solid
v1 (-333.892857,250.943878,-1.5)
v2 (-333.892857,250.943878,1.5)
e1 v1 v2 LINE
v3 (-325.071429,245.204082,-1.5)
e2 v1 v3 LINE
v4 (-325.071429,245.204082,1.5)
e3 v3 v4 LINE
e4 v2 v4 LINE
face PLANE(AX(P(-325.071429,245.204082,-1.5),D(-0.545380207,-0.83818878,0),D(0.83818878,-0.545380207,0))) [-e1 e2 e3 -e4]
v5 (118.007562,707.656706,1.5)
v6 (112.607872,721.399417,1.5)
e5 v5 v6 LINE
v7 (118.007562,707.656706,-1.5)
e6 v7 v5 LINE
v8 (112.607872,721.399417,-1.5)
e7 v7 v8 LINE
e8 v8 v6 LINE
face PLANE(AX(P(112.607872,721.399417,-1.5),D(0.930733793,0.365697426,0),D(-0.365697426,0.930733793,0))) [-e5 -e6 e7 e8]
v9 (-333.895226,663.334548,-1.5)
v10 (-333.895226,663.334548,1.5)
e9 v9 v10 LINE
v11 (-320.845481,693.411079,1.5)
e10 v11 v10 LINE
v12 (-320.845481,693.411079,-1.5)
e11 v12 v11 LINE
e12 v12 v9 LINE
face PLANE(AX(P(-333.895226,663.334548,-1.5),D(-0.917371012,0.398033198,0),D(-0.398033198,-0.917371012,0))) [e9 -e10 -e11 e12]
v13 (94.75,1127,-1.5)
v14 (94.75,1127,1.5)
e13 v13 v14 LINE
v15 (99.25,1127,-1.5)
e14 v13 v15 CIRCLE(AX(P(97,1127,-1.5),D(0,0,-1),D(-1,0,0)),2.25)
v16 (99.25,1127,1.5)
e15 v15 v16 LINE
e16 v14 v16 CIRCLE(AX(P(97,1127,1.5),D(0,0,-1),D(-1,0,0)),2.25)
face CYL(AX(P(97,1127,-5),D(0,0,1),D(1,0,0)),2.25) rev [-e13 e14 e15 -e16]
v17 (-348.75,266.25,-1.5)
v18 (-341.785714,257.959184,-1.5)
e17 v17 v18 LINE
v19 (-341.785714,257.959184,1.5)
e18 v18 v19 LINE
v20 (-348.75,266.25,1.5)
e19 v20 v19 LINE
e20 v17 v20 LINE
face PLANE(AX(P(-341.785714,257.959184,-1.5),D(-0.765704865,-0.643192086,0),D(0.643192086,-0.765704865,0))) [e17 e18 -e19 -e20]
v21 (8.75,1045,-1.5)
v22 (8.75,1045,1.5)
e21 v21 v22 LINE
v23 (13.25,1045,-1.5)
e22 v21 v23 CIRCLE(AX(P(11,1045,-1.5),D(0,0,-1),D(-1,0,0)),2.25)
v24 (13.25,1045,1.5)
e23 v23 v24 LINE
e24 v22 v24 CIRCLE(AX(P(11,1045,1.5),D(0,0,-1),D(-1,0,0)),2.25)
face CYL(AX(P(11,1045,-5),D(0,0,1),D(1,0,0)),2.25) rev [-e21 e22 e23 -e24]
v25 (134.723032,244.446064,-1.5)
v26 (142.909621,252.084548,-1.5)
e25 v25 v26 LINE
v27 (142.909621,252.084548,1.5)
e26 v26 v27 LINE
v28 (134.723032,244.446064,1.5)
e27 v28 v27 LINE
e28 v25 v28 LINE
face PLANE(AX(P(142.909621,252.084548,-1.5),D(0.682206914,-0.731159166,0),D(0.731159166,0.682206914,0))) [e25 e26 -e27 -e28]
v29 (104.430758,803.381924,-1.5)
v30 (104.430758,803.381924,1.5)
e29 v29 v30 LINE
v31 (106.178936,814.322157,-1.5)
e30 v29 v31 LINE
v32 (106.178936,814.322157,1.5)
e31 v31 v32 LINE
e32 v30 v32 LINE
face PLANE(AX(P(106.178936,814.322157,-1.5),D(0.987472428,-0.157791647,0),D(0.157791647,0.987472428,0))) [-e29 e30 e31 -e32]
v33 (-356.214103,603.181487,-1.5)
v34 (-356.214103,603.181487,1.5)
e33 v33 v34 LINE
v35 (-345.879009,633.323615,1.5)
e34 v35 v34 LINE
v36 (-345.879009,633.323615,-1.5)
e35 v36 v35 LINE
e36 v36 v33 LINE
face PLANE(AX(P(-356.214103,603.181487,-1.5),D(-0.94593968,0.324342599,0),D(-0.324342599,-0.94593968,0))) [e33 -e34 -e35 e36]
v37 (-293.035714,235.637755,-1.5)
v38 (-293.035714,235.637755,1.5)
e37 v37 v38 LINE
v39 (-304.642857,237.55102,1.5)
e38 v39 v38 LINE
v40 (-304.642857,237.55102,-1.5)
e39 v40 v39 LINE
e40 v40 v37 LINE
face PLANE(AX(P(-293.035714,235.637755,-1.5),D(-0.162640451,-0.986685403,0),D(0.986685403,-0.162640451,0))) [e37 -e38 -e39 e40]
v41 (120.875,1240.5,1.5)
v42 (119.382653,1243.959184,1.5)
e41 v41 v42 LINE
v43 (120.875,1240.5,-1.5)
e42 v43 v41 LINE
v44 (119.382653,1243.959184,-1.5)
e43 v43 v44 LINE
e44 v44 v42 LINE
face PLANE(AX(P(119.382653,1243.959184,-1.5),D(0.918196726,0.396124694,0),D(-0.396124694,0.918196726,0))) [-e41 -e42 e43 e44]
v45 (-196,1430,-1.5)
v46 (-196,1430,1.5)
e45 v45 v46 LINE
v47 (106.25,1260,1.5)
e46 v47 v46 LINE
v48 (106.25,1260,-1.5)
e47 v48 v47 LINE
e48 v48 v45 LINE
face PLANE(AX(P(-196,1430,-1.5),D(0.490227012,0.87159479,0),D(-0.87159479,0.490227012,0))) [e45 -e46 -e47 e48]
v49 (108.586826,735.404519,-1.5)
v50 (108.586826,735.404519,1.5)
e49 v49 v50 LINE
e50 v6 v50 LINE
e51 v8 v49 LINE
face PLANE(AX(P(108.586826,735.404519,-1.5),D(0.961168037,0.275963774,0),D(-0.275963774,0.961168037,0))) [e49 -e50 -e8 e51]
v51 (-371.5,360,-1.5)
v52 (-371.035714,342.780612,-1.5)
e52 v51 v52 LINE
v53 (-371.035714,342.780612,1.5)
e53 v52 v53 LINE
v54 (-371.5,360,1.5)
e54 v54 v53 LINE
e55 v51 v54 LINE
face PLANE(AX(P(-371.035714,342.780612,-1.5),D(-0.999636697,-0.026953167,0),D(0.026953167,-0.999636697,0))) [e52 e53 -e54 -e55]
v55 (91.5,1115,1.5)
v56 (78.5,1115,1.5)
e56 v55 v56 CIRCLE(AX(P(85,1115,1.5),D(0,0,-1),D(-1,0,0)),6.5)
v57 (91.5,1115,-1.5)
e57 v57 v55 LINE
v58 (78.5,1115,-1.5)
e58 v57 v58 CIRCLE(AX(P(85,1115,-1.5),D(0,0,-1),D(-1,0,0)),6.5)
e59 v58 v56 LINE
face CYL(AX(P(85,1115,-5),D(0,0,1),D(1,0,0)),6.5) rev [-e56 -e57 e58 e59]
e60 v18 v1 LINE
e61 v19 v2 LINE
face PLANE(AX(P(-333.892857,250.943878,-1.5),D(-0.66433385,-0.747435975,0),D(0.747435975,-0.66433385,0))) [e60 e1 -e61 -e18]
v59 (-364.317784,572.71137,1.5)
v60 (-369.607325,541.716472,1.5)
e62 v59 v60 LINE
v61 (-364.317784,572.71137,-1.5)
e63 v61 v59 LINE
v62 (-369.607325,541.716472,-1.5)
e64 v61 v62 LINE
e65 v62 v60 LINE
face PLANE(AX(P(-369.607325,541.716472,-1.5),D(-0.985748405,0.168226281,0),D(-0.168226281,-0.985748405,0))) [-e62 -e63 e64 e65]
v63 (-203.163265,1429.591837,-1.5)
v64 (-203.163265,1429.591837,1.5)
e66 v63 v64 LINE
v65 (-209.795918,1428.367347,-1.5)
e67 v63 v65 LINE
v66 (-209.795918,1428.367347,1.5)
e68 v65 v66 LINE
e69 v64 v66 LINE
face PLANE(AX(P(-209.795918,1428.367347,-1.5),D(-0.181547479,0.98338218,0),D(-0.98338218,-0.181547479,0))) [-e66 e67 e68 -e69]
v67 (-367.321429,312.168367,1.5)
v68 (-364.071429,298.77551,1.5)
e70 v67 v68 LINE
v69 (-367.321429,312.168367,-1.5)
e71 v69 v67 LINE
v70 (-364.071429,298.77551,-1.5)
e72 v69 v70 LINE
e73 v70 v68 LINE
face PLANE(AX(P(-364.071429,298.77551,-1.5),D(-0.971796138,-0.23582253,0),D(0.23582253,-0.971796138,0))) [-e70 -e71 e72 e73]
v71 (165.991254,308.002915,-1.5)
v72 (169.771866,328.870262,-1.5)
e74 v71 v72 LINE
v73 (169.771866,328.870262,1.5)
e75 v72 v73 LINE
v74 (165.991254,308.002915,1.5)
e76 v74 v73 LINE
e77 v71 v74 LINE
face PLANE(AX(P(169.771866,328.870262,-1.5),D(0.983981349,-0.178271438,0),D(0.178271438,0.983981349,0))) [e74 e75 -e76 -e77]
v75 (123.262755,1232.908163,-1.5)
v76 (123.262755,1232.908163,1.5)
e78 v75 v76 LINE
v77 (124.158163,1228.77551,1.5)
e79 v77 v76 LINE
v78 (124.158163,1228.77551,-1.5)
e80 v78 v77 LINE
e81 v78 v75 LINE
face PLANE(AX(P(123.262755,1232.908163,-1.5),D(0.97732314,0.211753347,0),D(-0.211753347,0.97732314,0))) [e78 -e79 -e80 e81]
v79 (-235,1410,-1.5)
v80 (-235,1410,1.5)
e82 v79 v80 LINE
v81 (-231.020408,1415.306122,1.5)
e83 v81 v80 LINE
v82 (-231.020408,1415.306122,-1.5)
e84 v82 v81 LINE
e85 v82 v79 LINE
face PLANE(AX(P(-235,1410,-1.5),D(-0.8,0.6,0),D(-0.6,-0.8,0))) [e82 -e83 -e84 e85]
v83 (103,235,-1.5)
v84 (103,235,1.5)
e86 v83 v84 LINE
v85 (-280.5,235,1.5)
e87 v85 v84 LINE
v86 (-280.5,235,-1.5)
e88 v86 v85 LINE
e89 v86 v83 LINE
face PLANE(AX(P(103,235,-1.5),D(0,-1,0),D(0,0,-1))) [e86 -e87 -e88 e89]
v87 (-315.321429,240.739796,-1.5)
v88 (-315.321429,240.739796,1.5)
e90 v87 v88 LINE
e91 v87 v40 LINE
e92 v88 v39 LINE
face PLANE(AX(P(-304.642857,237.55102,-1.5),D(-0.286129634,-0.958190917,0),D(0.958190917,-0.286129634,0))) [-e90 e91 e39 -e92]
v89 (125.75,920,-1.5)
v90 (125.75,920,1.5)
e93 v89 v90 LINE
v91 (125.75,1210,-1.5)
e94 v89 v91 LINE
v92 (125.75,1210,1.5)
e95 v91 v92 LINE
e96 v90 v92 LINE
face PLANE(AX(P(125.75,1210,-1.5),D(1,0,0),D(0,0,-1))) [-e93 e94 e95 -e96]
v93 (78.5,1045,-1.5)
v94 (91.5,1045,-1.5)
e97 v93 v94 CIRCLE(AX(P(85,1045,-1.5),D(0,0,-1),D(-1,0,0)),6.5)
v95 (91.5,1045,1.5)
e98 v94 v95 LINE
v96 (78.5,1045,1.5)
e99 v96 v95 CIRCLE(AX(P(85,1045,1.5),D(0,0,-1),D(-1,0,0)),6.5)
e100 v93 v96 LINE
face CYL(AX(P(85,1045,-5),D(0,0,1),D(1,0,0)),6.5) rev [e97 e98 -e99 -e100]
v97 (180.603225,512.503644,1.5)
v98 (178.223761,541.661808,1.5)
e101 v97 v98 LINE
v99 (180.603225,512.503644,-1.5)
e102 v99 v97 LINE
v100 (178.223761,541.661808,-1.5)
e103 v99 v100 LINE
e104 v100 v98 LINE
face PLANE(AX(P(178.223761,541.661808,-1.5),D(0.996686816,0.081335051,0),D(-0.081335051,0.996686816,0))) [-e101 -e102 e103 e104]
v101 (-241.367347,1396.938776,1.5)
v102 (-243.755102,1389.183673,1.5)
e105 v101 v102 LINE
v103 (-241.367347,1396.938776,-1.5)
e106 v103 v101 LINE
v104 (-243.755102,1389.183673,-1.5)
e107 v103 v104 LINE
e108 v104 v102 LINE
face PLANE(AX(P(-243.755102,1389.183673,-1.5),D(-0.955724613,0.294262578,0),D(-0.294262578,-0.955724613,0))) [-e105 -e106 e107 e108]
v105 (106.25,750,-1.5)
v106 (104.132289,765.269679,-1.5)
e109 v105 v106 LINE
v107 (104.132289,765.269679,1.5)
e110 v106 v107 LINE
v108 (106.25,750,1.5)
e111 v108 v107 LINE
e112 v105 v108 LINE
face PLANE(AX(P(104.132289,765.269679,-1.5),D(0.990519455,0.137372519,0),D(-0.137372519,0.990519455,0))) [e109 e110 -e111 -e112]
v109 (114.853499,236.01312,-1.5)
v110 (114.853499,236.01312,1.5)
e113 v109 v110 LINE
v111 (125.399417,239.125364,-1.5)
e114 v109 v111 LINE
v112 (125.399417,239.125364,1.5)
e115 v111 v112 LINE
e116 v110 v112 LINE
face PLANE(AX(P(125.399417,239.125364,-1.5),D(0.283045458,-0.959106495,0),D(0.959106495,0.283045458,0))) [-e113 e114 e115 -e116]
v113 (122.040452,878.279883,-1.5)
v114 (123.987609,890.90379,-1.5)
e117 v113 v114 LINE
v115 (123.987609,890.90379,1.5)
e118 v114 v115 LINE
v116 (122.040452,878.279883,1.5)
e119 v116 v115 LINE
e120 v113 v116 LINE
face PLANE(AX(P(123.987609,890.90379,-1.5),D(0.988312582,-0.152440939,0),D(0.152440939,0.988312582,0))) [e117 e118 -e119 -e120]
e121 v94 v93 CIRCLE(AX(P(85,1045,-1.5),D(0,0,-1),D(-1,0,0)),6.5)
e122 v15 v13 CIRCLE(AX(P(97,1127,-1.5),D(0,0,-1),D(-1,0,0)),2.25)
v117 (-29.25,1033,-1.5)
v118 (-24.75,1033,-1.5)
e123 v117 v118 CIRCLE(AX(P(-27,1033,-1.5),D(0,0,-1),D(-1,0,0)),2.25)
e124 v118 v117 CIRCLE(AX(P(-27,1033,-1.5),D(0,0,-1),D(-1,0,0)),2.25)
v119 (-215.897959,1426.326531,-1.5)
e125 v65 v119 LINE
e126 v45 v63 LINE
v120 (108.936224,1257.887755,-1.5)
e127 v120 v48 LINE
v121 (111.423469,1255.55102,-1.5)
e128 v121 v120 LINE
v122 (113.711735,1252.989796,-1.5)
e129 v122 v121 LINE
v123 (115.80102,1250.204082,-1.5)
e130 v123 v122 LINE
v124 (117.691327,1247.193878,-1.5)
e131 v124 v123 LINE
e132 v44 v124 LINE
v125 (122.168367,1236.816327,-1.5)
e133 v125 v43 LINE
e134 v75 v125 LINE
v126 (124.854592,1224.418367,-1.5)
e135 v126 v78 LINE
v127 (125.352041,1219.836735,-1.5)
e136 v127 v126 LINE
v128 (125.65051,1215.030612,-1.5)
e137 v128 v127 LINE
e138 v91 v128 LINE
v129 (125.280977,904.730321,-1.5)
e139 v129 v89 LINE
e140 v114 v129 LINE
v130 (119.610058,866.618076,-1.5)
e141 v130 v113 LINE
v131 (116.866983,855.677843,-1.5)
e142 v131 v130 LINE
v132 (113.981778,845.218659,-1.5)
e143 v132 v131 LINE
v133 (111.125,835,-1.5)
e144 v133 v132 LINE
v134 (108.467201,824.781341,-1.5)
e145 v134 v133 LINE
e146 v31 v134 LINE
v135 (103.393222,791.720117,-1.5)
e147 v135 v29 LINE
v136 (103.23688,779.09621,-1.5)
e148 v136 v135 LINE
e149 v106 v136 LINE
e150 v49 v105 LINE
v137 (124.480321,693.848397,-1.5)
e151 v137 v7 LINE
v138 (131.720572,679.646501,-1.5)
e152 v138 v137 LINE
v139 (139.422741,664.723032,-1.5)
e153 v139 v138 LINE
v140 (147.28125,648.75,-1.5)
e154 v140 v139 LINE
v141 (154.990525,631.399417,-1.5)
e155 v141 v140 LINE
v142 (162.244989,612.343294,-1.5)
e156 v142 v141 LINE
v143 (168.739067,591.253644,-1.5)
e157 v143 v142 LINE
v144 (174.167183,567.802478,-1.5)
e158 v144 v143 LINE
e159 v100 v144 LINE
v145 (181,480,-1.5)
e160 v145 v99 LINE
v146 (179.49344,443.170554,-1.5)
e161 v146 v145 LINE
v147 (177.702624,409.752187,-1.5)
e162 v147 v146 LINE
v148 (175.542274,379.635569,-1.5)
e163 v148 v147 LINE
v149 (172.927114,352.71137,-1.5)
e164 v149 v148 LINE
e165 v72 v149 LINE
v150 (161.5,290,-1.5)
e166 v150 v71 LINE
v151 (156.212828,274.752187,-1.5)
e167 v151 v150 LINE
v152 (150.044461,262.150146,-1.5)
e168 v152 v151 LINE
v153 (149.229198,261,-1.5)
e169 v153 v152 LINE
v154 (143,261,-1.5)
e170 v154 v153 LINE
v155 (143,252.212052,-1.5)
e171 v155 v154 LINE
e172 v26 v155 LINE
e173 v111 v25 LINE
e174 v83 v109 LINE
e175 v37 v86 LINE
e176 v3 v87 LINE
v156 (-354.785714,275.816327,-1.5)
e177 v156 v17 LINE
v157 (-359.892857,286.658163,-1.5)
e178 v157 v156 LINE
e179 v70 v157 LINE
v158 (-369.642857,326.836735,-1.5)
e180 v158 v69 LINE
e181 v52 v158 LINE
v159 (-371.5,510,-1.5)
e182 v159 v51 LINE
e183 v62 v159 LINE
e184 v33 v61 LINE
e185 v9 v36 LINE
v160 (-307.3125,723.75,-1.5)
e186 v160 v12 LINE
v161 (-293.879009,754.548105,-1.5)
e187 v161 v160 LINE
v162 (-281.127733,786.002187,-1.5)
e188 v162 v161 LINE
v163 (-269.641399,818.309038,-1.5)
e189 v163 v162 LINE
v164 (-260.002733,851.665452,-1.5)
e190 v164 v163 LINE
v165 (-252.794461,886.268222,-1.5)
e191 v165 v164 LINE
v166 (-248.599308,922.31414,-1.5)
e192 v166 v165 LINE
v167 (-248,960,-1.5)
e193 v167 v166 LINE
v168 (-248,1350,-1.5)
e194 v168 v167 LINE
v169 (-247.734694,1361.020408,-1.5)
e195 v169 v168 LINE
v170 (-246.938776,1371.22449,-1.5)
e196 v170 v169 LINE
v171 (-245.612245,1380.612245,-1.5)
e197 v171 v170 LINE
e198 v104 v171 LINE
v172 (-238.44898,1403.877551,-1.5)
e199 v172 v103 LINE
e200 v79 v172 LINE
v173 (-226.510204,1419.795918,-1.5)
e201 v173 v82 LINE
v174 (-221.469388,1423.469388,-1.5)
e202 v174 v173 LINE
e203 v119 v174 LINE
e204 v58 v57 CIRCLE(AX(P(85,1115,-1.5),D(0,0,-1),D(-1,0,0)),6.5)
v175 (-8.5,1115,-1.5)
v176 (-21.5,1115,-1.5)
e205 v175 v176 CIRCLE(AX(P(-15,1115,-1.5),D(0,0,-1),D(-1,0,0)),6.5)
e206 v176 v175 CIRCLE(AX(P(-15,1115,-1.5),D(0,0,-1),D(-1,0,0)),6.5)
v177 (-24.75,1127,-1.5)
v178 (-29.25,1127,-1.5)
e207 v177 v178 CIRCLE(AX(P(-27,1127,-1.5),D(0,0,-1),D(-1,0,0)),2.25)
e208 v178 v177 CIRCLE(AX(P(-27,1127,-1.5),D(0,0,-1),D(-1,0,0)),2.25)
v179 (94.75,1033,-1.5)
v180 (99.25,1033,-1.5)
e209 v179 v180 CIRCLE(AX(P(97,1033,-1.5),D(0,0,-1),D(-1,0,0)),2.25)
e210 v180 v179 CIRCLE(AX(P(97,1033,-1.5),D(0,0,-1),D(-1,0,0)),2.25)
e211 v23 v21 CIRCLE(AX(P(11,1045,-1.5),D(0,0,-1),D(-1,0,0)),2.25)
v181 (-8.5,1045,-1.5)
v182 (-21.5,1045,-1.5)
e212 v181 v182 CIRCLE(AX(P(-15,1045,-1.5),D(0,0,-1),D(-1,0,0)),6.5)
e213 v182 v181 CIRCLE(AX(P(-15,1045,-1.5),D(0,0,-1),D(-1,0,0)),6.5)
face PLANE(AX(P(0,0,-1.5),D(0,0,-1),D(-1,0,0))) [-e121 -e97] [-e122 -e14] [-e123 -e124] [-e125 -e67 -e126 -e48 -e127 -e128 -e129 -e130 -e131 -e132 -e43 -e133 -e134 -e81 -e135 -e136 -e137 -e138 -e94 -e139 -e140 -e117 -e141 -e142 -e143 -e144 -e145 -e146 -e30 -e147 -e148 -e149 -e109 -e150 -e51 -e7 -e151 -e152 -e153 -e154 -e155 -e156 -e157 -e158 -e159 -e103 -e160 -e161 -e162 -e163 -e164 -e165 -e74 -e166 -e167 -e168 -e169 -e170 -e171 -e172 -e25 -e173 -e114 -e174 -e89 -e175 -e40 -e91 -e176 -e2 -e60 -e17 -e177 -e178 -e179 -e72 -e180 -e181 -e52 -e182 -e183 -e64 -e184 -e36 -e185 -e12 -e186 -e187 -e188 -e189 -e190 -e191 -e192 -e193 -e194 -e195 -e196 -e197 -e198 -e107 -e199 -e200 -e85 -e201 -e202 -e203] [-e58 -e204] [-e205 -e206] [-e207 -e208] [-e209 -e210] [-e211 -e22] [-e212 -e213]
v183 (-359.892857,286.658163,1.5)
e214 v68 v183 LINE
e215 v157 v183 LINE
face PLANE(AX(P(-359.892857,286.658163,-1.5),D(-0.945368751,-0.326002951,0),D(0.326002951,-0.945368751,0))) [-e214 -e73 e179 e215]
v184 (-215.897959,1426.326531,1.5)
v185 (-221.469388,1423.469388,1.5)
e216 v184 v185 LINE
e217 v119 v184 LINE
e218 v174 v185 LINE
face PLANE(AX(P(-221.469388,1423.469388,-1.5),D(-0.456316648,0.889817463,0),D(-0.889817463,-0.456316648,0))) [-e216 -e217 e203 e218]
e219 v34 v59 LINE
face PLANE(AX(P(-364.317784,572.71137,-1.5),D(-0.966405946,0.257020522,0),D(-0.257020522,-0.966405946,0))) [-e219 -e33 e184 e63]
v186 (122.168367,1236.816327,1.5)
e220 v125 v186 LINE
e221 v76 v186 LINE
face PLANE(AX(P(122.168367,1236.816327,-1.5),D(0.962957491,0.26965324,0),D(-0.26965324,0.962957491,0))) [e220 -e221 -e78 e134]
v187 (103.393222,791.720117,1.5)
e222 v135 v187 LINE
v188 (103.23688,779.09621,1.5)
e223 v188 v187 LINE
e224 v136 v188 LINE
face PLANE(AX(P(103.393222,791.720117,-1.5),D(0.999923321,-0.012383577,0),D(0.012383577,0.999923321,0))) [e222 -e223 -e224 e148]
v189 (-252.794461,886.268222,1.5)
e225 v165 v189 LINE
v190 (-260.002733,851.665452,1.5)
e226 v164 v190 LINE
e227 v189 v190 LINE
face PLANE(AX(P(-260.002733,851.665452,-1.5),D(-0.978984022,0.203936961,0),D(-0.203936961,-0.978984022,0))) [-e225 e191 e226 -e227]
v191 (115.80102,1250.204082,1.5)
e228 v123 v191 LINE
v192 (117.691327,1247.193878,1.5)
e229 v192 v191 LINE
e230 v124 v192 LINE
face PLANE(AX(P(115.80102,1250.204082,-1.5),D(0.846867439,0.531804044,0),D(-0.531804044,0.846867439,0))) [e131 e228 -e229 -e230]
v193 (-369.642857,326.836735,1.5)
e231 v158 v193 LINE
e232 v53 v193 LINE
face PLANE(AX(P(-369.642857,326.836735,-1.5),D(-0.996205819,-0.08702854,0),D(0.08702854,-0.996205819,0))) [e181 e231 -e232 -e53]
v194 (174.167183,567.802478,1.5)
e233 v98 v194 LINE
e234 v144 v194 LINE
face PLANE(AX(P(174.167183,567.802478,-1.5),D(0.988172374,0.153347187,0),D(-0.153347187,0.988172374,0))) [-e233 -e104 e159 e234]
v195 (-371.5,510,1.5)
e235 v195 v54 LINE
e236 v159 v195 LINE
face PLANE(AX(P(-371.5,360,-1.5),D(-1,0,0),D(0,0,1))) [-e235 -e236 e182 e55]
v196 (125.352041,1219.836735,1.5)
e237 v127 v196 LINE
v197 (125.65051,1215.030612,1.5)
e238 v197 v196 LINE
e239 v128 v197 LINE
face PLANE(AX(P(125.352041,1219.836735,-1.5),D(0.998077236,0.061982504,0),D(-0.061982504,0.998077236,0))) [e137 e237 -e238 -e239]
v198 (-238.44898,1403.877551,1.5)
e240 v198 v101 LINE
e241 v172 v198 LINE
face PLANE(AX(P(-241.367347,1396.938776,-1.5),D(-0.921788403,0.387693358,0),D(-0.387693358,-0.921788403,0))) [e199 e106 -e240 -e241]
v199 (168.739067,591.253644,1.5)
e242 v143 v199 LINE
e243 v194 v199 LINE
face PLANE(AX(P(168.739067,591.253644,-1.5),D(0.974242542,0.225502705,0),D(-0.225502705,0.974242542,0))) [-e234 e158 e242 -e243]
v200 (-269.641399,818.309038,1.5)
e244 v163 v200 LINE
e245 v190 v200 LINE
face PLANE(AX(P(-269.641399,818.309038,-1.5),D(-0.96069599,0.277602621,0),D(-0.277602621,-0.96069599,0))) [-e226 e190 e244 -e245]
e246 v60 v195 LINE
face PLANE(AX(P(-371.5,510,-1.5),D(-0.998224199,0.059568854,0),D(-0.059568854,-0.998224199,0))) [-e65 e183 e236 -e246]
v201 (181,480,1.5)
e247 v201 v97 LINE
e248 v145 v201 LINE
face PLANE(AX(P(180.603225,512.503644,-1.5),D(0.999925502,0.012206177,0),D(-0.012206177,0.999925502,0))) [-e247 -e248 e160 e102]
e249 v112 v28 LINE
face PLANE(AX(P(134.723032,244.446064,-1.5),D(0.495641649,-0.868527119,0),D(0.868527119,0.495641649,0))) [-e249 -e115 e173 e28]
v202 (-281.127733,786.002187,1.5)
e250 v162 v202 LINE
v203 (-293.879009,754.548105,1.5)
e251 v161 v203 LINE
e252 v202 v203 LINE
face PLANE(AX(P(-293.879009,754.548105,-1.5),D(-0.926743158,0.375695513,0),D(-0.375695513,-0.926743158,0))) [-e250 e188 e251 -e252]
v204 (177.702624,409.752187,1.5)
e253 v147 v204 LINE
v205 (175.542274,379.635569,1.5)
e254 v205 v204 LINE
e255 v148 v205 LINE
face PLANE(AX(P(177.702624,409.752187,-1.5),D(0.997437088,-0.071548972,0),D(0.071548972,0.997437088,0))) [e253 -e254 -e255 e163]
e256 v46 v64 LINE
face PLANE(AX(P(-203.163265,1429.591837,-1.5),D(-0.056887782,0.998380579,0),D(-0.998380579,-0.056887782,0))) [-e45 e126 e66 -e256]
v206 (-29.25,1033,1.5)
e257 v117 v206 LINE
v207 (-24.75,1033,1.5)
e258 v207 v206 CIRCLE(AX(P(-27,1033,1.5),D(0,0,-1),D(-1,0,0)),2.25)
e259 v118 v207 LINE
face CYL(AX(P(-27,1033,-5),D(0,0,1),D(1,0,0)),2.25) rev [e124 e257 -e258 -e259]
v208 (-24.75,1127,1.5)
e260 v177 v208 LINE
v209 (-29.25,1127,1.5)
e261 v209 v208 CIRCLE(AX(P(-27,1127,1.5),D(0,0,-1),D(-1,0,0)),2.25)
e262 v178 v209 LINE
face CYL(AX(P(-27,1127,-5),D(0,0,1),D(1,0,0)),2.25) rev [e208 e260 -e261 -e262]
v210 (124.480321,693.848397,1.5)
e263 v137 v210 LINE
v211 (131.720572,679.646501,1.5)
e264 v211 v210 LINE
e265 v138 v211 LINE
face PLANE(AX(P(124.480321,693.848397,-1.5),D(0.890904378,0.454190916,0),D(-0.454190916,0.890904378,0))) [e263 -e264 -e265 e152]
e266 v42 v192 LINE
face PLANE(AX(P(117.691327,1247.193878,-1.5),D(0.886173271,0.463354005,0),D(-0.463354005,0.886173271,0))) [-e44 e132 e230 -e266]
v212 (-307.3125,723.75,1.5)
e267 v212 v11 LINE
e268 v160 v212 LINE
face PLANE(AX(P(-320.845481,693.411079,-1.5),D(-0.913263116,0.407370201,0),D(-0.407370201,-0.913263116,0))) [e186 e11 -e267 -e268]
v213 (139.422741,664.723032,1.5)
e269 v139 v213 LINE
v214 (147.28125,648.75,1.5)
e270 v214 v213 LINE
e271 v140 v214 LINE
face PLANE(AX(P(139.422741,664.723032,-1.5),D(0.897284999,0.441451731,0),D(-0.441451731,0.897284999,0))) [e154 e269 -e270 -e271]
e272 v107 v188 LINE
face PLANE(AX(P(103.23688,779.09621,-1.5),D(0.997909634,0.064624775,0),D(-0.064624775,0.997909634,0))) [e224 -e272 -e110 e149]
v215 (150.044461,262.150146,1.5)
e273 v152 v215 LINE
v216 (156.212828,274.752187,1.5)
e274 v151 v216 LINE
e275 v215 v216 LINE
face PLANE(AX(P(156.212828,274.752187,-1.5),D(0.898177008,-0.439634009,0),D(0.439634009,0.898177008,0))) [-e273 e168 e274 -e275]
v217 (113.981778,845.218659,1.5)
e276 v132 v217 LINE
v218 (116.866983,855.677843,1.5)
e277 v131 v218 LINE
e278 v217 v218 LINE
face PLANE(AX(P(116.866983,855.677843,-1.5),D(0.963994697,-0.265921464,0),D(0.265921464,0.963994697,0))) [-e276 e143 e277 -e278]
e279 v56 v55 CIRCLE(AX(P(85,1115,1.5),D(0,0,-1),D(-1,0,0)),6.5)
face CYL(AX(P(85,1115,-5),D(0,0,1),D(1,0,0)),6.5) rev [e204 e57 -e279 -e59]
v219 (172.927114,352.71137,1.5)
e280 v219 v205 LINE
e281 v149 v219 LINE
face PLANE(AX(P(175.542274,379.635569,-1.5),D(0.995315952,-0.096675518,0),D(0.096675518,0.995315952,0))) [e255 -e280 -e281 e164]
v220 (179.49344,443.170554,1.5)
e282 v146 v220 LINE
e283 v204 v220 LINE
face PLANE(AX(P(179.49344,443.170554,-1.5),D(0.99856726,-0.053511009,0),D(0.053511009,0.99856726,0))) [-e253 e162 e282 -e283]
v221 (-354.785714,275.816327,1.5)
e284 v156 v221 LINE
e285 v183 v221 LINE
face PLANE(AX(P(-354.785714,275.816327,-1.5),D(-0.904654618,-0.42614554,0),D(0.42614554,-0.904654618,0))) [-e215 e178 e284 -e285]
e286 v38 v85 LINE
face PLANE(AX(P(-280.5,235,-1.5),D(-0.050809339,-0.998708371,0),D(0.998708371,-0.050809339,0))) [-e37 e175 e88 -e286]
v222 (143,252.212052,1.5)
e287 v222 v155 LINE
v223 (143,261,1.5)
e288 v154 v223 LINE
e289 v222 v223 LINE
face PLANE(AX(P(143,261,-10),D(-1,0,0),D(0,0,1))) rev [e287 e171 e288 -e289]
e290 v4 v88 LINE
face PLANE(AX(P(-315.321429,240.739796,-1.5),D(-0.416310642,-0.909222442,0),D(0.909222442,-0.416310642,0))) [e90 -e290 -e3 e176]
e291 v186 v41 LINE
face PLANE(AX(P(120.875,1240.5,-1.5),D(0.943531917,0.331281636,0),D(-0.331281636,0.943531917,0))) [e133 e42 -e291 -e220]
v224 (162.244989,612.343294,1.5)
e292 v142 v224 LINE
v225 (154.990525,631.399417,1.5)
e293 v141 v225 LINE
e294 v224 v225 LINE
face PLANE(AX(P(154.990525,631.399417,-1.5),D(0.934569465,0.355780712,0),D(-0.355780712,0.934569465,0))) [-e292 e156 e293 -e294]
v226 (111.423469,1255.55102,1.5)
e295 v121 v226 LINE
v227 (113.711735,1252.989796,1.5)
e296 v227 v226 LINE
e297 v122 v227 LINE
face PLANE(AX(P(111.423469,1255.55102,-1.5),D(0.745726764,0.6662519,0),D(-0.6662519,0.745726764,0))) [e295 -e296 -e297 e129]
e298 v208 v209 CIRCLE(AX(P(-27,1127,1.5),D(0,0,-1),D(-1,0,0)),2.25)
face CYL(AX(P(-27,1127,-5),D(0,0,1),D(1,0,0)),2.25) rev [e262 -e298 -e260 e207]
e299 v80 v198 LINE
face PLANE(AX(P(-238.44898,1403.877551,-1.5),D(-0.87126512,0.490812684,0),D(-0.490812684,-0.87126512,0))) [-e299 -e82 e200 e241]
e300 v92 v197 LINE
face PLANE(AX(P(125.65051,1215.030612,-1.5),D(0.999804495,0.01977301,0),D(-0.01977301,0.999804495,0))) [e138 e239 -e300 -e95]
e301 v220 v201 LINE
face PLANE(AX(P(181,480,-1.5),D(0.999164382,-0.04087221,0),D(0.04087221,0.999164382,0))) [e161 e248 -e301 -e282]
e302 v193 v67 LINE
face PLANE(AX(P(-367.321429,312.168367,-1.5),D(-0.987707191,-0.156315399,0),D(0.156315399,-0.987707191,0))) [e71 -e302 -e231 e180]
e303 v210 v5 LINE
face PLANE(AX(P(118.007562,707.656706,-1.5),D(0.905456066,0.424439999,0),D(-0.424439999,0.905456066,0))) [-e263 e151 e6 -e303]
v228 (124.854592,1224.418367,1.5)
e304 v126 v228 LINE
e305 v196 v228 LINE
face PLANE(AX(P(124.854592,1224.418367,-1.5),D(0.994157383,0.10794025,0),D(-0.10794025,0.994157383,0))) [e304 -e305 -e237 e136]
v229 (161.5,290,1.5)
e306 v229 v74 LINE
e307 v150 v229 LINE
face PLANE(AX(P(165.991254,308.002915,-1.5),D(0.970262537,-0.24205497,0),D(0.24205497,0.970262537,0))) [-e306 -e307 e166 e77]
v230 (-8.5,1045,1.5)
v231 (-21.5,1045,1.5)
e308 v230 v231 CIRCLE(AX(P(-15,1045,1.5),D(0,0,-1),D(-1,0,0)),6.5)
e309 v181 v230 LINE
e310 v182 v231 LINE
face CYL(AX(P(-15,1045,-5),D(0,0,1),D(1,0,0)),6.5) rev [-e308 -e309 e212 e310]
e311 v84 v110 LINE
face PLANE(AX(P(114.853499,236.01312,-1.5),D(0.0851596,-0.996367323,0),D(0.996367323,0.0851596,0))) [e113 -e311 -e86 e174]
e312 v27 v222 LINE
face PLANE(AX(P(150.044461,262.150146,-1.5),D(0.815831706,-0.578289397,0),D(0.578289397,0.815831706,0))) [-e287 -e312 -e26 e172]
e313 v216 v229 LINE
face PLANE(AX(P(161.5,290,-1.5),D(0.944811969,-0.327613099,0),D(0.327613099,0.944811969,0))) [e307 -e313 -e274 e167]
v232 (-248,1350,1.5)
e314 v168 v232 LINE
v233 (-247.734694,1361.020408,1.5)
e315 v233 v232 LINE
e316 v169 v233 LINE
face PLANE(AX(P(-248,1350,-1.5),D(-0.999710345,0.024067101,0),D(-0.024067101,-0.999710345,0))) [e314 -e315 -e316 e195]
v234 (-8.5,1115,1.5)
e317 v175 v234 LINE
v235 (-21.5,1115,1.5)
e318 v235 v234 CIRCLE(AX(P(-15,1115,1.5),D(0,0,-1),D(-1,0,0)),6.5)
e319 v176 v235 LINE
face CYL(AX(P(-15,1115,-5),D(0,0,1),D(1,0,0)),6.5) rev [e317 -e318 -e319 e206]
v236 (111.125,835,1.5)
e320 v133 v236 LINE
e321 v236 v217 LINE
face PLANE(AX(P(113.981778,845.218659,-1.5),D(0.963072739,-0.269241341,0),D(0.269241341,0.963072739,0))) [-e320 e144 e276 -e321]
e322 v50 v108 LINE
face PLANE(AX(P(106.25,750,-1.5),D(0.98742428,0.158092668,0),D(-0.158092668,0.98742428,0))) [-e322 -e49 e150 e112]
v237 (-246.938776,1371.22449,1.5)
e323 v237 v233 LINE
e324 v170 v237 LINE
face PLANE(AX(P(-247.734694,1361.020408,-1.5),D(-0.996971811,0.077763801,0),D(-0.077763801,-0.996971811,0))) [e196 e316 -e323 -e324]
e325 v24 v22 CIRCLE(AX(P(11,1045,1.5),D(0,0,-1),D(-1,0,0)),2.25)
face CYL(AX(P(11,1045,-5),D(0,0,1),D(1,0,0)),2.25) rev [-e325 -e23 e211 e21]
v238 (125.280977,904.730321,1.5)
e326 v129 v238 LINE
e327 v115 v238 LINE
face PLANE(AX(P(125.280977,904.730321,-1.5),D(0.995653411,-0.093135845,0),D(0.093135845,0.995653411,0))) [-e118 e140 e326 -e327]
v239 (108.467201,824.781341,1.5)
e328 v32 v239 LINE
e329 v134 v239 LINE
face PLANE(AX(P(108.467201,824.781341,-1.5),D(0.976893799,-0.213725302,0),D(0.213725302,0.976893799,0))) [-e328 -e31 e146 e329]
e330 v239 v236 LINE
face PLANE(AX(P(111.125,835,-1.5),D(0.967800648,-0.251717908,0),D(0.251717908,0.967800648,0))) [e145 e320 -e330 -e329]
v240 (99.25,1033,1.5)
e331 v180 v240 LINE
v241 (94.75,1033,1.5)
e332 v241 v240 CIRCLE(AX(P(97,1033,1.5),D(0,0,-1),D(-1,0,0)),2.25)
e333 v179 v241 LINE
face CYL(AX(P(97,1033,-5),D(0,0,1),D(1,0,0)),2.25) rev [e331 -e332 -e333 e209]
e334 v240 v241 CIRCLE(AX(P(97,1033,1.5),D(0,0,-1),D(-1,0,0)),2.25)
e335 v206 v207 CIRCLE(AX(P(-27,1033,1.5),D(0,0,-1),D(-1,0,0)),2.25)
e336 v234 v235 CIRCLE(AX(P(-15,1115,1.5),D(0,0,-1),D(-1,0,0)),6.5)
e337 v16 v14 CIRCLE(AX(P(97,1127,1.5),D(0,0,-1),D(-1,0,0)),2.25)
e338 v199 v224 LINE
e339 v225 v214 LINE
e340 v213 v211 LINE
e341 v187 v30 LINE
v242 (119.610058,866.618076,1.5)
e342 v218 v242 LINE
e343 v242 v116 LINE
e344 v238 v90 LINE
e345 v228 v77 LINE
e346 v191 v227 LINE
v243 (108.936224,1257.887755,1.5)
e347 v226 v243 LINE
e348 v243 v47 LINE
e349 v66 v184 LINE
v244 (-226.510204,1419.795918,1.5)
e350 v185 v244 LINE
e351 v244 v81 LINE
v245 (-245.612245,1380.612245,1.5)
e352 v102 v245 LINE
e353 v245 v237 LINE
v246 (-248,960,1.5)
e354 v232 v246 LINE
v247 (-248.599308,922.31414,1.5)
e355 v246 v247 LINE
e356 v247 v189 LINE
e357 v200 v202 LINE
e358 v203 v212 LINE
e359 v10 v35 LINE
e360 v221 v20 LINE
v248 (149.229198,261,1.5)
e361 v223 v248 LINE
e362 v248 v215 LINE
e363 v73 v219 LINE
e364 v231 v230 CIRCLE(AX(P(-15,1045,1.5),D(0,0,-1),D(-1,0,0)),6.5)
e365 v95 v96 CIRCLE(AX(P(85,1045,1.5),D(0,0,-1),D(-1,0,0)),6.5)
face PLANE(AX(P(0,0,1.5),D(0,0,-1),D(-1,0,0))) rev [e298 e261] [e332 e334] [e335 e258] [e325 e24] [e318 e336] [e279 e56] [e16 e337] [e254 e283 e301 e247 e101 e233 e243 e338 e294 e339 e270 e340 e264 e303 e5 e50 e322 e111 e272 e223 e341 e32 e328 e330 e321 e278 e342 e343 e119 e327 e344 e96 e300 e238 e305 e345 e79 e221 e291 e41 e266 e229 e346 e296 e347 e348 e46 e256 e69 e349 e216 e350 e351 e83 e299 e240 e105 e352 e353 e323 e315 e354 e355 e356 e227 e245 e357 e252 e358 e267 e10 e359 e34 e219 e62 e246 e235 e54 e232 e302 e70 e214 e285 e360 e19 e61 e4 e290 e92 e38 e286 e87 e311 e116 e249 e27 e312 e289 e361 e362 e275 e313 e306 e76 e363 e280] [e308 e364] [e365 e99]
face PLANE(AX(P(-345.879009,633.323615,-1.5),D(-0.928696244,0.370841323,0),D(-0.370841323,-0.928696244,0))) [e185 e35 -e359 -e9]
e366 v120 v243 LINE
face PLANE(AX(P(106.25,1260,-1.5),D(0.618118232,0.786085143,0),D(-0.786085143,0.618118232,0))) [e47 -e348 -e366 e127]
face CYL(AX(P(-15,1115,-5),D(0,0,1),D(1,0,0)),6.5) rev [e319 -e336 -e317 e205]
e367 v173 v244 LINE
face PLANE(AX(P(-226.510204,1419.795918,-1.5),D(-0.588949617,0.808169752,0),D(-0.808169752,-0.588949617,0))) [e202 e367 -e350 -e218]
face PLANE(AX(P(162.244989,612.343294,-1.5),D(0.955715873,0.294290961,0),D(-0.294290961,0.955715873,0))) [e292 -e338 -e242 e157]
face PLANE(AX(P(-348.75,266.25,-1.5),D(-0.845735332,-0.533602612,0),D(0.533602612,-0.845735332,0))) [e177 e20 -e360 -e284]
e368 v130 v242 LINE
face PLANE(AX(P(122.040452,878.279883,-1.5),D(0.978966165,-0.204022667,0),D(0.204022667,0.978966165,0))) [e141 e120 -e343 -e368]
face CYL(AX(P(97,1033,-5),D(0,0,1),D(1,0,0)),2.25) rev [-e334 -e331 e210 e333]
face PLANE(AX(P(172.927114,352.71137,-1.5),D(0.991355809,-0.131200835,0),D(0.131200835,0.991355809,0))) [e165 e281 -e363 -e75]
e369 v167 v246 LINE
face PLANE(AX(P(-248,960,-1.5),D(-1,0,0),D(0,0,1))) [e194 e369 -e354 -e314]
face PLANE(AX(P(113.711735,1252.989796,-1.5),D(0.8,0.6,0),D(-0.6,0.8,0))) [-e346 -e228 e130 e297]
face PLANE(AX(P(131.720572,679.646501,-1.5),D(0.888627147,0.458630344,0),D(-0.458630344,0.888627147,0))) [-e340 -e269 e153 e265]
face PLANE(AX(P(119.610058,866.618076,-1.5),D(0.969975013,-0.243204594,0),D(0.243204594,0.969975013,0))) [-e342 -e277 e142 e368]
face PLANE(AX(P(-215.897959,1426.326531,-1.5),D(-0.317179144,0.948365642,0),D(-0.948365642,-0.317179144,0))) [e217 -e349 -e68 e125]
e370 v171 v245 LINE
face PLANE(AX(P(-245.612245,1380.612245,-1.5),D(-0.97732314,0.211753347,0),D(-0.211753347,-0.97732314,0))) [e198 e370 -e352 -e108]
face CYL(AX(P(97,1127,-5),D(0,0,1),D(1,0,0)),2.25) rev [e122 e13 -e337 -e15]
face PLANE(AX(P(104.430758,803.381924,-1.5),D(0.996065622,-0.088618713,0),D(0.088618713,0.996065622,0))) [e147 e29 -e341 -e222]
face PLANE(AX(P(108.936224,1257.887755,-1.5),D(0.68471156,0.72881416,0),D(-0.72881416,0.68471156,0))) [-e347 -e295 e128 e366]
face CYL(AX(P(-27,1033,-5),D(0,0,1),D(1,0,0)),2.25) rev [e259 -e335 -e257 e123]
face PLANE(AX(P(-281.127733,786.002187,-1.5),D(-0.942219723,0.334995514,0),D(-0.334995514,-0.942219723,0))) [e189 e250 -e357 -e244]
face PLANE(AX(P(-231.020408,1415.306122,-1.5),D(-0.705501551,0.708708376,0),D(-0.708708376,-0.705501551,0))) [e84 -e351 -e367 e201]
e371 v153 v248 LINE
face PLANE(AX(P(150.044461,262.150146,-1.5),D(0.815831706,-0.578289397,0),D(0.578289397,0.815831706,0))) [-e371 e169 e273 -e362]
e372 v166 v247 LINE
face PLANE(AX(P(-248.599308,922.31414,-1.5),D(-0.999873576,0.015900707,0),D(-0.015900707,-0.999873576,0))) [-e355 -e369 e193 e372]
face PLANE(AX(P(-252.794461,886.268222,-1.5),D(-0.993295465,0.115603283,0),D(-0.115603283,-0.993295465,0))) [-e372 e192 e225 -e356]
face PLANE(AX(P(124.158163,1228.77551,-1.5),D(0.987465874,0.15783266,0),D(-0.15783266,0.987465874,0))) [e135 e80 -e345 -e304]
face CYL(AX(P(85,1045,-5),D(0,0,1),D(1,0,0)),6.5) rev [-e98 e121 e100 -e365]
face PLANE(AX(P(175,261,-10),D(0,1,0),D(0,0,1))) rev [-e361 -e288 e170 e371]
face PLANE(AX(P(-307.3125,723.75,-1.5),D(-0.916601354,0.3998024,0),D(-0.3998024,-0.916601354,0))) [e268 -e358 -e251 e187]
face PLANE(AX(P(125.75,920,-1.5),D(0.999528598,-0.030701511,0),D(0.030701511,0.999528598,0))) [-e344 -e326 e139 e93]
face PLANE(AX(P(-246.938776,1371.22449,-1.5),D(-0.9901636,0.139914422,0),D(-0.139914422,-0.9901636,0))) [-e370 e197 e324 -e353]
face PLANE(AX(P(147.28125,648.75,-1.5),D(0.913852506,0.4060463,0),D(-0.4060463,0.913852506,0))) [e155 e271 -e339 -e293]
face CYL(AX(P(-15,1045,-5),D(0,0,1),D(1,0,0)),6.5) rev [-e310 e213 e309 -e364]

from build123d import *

# Parameters (mm, degrees)
EXTRUDE_1_DEPTH     = 1.5
SKETCH_2_W          = 32
SKETCH_2_H          = 22
CUT_EXTRUDE_1_DEPTH = 10
SKETCH_3_R          = 2.25
SKETCH_3_R_2        = 6.5
CUT_EXTRUDE_2_DEPTH = 5


with BuildPart() as part:
    # 草图1 → 凸台-拉伸1 (new, symmetric)
    with BuildSketch(Plane.XY):
        Polygon((103, 235), (-24.833333333, 235), (-152.666666667, 235), (-280.5, 235), (-293.035714286, 235.637755102), (-304.642857143, 237.551020408), (-315.321428571, 240.739795918), (-325.071428571, 245.204081633), (-333.892857143, 250.943877551), (-341.785714286, 257.959183673), (-348.75, 266.25), (-354.785714286, 275.816326531), (-359.892857143, 286.658163265), (-364.071428571, 298.775510204), (-367.321428571, 312.168367347), (-369.642857143, 326.836734694), (-371.035714286, 342.780612245), (-371.5, 360), (-371.5, 410), (-371.5, 460), (-371.5, 510), (-369.607325073, 541.716472303), (-364.317784257, 572.711370262), (-356.214103499, 603.18148688), (-345.879008746, 633.32361516), (-333.895225948, 663.334548105), (-320.84548105, 693.411078717), (-307.3125, 723.75), (-293.879008746, 754.548104956), (-281.127733236, 786.002186589), (-269.641399417, 818.309037901), (-260.002733236, 851.665451895), (-252.794460641, 886.268221574), (-248.59930758, 922.314139942), (-248, 960), (-248, 1090), (-248, 1220), (-248, 1350), (-247.734693878, 1361.020408163), (-246.93877551, 1371.224489796), (-245.612244898, 1380.612244898), (-243.755102041, 1389.183673469), (-241.367346939, 1396.93877551), (-238.448979592, 1403.87755102), (-235, 1410), (-231.020408163, 1415.306122449), (-226.510204082, 1419.795918367), (-221.469387755, 1423.469387755), (-215.897959184, 1426.326530612), (-209.795918367, 1428.367346939), (-203.163265306, 1429.591836735), (-196, 1430), (-95.25, 1373.333333333), (5.5, 1316.666666667), (106.25, 1260), (108.93622449, 1257.887755102), (111.423469388, 1255.551020408), (113.711734694, 1252.989795918), (115.801020408, 1250.204081633), (117.691326531, 1247.193877551), (119.382653061, 1243.959183673), (120.875, 1240.5), (122.168367347, 1236.816326531), (123.262755102, 1232.908163265), (124.158163265, 1228.775510204), (124.854591837, 1224.418367347), (125.352040816, 1219.836734694), (125.650510204, 1215.030612245), (125.75, 1210), (125.75, 1113.333333333), (125.75, 1016.666666667), (125.75, 920), (125.280976676, 904.7303207), (123.987609329, 890.903790087), (122.040451895, 878.279883382), (119.610058309, 866.618075802), (116.866982507, 855.677842566), (113.981778426, 845.218658892), (111.125, 835), (108.467201166, 824.781341108), (106.17893586, 814.322157434), (104.430758017, 803.381924198), (103.393221574, 791.720116618), (103.236880466, 779.096209913), (104.13228863, 765.2696793), (106.25, 750), (108.586825802, 735.40451895), (112.60787172, 721.39941691), (118.007561953, 707.656705539), (124.4803207, 693.848396501), (131.720572157, 679.646501458), (139.422740525, 664.72303207), (147.28125, 648.75), (154.990524781, 631.39941691), (162.244989067, 612.343294461), (168.739067055, 591.253644315), (174.167182945, 567.802478134), (178.223760933, 541.66180758), (180.603225219, 512.503644315), (181, 480), (179.493440233, 443.170553936), (177.702623907, 409.752186589), (175.542274052, 379.635568513), (172.927113703, 352.711370262), (169.771865889, 328.870262391), (165.991253644, 308.002915452), (161.5, 290), (156.212827988, 274.752186589), (150.044460641, 262.150145773), (142.909620991, 252.084548105), (134.72303207, 244.44606414), (125.39941691, 239.125364431), (114.853498542, 236.013119534), align=None)
    extrude(amount=EXTRUDE_1_DEPTH, both=True)

    # 草图2 → 切除-拉伸1 (cut, symmetric)
    with BuildSketch(Plane.XY):
        with Locations((159, 250)):
            Rectangle(SKETCH_2_W, SKETCH_2_H)
        with Locations((159, 1150)):
            Rectangle(SKETCH_2_W, SKETCH_2_H)
    extrude(amount=CUT_EXTRUDE_1_DEPTH, both=True, mode=Mode.SUBTRACT)

    # 草图3 → 切除-拉伸2 (cut, symmetric)
    with BuildSketch(Plane.XY):
        with Locations(Location((-27, 1127, 0), (0, 0, 180))):
            Circle(SKETCH_3_R)
        with Locations(Location((-27, 1033, 0), (0, 0, 180))):
            Circle(SKETCH_3_R)
        with Locations(Location((97, 1127, 0), (0, 0, 180))):
            Circle(SKETCH_3_R)
        with Locations(Location((97, 1033, 0), (0, 0, 180))):
            Circle(SKETCH_3_R)
        with Locations(Location((-15, 1115, 0), (0, 0, 180))):
            Circle(SKETCH_3_R_2)
        with Locations(Location((-15, 1045, 0), (0, 0, 180))):
            Circle(SKETCH_3_R_2)
        with Locations(Location((85, 1115, 0), (0, 0, 180))):
            Circle(SKETCH_3_R_2)
        with Locations(Location((85, 1045, 0), (0, 0, 180))):
            Circle(SKETCH_3_R_2)
        with Locations(Location((11, 1045, 0), (0, 0, 180))):
            Circle(SKETCH_3_R)
    extrude(amount=CUT_EXTRUDE_2_DEPTH, both=True, mode=Mode.SUBTRACT)


solid = part.part
